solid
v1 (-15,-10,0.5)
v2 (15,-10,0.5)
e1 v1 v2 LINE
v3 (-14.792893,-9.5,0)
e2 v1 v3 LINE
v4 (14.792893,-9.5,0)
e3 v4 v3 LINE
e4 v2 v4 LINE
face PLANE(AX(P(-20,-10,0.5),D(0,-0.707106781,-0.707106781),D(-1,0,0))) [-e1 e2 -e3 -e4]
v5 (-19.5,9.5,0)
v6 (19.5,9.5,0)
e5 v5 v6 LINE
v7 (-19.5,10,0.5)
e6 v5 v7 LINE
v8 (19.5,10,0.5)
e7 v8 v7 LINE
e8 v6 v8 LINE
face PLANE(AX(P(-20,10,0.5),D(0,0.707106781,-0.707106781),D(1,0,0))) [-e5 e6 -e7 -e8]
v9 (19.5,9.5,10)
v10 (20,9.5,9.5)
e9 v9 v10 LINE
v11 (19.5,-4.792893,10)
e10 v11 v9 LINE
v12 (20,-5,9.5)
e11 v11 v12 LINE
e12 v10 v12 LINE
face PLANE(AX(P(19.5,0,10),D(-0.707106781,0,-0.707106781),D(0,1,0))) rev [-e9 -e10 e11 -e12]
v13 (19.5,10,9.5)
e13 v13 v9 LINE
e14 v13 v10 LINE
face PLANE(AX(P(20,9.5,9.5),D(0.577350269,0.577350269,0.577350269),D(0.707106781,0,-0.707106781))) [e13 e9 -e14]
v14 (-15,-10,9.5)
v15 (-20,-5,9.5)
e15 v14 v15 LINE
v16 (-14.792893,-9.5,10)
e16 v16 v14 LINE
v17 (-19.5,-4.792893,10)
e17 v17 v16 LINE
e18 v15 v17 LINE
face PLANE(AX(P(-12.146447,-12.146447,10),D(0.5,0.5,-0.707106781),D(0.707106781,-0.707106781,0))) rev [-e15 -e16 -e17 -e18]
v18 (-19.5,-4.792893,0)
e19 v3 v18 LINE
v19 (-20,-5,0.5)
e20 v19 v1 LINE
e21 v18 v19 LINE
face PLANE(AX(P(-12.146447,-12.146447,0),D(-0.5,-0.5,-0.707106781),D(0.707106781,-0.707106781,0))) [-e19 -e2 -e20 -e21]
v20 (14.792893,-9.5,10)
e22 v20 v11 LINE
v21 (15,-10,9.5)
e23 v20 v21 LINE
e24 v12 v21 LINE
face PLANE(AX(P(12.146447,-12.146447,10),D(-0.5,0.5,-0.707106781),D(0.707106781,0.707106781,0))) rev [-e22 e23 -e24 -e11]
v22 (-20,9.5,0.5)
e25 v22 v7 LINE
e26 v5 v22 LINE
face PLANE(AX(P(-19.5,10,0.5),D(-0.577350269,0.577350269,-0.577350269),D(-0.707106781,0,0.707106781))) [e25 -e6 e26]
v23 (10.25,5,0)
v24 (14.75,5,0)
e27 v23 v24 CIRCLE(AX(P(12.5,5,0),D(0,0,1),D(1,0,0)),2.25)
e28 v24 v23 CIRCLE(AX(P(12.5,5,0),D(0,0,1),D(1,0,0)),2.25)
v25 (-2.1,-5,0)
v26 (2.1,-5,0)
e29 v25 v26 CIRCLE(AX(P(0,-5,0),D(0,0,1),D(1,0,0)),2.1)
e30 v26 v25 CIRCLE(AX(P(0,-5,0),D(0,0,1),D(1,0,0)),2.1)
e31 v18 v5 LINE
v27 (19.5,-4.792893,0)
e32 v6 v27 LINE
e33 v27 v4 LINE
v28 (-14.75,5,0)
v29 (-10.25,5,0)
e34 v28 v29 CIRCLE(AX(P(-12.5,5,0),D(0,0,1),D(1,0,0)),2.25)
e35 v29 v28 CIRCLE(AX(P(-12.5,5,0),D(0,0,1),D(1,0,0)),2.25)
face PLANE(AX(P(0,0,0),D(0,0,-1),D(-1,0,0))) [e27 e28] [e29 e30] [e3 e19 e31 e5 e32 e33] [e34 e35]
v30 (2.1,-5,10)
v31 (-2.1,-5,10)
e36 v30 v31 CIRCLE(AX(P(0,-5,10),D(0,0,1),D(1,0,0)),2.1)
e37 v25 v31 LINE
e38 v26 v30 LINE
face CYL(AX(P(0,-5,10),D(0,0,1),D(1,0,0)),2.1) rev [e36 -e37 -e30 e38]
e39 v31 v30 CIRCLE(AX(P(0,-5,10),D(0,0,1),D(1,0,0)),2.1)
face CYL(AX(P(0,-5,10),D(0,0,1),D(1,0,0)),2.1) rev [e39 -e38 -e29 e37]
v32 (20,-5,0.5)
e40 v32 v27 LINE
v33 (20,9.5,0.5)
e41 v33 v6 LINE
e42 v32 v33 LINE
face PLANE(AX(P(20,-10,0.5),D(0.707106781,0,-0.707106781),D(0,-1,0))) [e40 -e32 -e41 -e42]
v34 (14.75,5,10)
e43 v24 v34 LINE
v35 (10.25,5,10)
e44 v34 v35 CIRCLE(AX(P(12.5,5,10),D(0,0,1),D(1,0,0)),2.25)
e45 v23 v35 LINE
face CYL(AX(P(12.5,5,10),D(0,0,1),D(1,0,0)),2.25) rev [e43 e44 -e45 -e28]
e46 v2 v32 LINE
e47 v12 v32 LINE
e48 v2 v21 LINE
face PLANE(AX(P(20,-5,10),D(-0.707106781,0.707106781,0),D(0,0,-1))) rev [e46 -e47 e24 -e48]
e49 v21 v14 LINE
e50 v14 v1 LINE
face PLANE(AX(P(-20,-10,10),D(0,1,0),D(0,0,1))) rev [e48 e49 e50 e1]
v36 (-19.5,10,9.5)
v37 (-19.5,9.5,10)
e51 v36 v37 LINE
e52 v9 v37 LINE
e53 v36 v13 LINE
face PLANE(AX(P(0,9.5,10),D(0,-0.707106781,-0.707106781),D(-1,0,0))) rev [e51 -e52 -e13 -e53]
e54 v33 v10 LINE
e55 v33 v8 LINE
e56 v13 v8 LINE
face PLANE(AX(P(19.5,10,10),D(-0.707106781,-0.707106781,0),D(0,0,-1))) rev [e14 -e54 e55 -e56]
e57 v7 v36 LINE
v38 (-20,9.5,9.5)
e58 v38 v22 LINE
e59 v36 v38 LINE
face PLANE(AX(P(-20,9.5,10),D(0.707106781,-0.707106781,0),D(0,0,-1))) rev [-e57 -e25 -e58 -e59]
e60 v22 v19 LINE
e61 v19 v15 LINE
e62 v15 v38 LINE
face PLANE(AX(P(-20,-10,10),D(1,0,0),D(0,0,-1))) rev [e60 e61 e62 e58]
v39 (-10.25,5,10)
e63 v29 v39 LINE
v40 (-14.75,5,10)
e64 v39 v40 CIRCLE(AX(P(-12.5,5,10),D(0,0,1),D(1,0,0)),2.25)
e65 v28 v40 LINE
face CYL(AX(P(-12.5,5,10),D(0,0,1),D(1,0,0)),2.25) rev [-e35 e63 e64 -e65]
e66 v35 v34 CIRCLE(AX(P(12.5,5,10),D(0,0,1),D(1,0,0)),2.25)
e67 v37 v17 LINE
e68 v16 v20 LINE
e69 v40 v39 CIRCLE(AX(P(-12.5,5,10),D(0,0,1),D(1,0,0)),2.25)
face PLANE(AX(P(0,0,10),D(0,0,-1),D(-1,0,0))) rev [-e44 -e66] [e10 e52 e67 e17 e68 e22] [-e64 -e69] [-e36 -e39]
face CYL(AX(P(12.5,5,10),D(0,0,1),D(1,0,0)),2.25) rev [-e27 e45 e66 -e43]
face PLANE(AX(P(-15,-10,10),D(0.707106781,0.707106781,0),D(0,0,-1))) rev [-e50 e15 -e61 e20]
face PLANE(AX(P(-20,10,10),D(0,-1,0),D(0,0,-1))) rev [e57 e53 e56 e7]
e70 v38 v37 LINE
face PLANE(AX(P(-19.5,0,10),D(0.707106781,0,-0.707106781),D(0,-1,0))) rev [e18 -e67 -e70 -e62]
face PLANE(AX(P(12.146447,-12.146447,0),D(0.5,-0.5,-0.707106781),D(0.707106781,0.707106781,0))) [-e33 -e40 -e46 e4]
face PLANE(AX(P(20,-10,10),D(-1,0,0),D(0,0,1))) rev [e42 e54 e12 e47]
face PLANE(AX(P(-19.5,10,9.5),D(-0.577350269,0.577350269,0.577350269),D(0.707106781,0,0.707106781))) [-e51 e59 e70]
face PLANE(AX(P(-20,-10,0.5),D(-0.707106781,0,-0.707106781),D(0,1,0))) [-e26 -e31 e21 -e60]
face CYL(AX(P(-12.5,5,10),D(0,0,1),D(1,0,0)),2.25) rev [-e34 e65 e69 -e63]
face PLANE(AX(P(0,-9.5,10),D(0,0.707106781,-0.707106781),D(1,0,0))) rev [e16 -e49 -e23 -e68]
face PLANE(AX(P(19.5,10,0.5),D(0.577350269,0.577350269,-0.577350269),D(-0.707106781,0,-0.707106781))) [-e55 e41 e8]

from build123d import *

# Parameters (mm, degrees)
SKETCH_1_W              = 40
SKETCH_1_H              = 20
EXTRUDE_1_DEPTH         = 10
HOLE_WIZARD_4_5_4_5_1_D = 4.5
HOLE_WIZARD_M5_1_D      = 4.2
CHAMFER_1_SIZE          = 5
CHAMFER_2_SIZE          = 0.5


with BuildPart() as part:
    # 草图1 → 凸台-拉伸1 (new body)
    with BuildSketch(Plane.XY):
        Rectangle(SKETCH_1_W, SKETCH_1_H)
    extrude(amount=EXTRUDE_1_DEPTH)

    # Ø4.5 (4.5) 直径孔1 (through all)
    with Locations(Plane.XY.offset(10)):
        with Locations((12.5, 5), (-12.5, 5)):
            Hole(HOLE_WIZARD_4_5_4_5_1_D / 2)

    # M5 螺纹孔1 (through all)
    with Locations(Plane.XY.offset(10)):
        with Locations((0, -5)):
            Hole(HOLE_WIZARD_M5_1_D / 2)

    # 倒角1
    chamfer_1_edges = [part.edges().sort_by_distance(p)[0] for p in [
        (20, -10, 5),
        (-20, -10, 5),
    ]]
    chamfer(chamfer_1_edges, length=CHAMFER_1_SIZE)

    # 倒角2
    chamfer_2_edges = [part.edges().sort_by_distance(p)[0] for p in [
        (-20, 2.5, 10),
        (0, -10, 0),
        (0, -10, 10),
        (20, 2.5, 0),
        (17.5, -7.5, 0),
        (-17.5, -7.5, 0),
        (20, 2.5, 10),
        (17.5, -7.5, 10),
        (-17.5, -7.5, 10),
        (-20, 2.5, 0),
        (0, 10, 0),
        (-20, 10, 5),
        (20, 10, 5),
        (0, 10, 10),
    ]]
    chamfer(chamfer_2_edges, length=CHAMFER_2_SIZE)


solid = part.part
